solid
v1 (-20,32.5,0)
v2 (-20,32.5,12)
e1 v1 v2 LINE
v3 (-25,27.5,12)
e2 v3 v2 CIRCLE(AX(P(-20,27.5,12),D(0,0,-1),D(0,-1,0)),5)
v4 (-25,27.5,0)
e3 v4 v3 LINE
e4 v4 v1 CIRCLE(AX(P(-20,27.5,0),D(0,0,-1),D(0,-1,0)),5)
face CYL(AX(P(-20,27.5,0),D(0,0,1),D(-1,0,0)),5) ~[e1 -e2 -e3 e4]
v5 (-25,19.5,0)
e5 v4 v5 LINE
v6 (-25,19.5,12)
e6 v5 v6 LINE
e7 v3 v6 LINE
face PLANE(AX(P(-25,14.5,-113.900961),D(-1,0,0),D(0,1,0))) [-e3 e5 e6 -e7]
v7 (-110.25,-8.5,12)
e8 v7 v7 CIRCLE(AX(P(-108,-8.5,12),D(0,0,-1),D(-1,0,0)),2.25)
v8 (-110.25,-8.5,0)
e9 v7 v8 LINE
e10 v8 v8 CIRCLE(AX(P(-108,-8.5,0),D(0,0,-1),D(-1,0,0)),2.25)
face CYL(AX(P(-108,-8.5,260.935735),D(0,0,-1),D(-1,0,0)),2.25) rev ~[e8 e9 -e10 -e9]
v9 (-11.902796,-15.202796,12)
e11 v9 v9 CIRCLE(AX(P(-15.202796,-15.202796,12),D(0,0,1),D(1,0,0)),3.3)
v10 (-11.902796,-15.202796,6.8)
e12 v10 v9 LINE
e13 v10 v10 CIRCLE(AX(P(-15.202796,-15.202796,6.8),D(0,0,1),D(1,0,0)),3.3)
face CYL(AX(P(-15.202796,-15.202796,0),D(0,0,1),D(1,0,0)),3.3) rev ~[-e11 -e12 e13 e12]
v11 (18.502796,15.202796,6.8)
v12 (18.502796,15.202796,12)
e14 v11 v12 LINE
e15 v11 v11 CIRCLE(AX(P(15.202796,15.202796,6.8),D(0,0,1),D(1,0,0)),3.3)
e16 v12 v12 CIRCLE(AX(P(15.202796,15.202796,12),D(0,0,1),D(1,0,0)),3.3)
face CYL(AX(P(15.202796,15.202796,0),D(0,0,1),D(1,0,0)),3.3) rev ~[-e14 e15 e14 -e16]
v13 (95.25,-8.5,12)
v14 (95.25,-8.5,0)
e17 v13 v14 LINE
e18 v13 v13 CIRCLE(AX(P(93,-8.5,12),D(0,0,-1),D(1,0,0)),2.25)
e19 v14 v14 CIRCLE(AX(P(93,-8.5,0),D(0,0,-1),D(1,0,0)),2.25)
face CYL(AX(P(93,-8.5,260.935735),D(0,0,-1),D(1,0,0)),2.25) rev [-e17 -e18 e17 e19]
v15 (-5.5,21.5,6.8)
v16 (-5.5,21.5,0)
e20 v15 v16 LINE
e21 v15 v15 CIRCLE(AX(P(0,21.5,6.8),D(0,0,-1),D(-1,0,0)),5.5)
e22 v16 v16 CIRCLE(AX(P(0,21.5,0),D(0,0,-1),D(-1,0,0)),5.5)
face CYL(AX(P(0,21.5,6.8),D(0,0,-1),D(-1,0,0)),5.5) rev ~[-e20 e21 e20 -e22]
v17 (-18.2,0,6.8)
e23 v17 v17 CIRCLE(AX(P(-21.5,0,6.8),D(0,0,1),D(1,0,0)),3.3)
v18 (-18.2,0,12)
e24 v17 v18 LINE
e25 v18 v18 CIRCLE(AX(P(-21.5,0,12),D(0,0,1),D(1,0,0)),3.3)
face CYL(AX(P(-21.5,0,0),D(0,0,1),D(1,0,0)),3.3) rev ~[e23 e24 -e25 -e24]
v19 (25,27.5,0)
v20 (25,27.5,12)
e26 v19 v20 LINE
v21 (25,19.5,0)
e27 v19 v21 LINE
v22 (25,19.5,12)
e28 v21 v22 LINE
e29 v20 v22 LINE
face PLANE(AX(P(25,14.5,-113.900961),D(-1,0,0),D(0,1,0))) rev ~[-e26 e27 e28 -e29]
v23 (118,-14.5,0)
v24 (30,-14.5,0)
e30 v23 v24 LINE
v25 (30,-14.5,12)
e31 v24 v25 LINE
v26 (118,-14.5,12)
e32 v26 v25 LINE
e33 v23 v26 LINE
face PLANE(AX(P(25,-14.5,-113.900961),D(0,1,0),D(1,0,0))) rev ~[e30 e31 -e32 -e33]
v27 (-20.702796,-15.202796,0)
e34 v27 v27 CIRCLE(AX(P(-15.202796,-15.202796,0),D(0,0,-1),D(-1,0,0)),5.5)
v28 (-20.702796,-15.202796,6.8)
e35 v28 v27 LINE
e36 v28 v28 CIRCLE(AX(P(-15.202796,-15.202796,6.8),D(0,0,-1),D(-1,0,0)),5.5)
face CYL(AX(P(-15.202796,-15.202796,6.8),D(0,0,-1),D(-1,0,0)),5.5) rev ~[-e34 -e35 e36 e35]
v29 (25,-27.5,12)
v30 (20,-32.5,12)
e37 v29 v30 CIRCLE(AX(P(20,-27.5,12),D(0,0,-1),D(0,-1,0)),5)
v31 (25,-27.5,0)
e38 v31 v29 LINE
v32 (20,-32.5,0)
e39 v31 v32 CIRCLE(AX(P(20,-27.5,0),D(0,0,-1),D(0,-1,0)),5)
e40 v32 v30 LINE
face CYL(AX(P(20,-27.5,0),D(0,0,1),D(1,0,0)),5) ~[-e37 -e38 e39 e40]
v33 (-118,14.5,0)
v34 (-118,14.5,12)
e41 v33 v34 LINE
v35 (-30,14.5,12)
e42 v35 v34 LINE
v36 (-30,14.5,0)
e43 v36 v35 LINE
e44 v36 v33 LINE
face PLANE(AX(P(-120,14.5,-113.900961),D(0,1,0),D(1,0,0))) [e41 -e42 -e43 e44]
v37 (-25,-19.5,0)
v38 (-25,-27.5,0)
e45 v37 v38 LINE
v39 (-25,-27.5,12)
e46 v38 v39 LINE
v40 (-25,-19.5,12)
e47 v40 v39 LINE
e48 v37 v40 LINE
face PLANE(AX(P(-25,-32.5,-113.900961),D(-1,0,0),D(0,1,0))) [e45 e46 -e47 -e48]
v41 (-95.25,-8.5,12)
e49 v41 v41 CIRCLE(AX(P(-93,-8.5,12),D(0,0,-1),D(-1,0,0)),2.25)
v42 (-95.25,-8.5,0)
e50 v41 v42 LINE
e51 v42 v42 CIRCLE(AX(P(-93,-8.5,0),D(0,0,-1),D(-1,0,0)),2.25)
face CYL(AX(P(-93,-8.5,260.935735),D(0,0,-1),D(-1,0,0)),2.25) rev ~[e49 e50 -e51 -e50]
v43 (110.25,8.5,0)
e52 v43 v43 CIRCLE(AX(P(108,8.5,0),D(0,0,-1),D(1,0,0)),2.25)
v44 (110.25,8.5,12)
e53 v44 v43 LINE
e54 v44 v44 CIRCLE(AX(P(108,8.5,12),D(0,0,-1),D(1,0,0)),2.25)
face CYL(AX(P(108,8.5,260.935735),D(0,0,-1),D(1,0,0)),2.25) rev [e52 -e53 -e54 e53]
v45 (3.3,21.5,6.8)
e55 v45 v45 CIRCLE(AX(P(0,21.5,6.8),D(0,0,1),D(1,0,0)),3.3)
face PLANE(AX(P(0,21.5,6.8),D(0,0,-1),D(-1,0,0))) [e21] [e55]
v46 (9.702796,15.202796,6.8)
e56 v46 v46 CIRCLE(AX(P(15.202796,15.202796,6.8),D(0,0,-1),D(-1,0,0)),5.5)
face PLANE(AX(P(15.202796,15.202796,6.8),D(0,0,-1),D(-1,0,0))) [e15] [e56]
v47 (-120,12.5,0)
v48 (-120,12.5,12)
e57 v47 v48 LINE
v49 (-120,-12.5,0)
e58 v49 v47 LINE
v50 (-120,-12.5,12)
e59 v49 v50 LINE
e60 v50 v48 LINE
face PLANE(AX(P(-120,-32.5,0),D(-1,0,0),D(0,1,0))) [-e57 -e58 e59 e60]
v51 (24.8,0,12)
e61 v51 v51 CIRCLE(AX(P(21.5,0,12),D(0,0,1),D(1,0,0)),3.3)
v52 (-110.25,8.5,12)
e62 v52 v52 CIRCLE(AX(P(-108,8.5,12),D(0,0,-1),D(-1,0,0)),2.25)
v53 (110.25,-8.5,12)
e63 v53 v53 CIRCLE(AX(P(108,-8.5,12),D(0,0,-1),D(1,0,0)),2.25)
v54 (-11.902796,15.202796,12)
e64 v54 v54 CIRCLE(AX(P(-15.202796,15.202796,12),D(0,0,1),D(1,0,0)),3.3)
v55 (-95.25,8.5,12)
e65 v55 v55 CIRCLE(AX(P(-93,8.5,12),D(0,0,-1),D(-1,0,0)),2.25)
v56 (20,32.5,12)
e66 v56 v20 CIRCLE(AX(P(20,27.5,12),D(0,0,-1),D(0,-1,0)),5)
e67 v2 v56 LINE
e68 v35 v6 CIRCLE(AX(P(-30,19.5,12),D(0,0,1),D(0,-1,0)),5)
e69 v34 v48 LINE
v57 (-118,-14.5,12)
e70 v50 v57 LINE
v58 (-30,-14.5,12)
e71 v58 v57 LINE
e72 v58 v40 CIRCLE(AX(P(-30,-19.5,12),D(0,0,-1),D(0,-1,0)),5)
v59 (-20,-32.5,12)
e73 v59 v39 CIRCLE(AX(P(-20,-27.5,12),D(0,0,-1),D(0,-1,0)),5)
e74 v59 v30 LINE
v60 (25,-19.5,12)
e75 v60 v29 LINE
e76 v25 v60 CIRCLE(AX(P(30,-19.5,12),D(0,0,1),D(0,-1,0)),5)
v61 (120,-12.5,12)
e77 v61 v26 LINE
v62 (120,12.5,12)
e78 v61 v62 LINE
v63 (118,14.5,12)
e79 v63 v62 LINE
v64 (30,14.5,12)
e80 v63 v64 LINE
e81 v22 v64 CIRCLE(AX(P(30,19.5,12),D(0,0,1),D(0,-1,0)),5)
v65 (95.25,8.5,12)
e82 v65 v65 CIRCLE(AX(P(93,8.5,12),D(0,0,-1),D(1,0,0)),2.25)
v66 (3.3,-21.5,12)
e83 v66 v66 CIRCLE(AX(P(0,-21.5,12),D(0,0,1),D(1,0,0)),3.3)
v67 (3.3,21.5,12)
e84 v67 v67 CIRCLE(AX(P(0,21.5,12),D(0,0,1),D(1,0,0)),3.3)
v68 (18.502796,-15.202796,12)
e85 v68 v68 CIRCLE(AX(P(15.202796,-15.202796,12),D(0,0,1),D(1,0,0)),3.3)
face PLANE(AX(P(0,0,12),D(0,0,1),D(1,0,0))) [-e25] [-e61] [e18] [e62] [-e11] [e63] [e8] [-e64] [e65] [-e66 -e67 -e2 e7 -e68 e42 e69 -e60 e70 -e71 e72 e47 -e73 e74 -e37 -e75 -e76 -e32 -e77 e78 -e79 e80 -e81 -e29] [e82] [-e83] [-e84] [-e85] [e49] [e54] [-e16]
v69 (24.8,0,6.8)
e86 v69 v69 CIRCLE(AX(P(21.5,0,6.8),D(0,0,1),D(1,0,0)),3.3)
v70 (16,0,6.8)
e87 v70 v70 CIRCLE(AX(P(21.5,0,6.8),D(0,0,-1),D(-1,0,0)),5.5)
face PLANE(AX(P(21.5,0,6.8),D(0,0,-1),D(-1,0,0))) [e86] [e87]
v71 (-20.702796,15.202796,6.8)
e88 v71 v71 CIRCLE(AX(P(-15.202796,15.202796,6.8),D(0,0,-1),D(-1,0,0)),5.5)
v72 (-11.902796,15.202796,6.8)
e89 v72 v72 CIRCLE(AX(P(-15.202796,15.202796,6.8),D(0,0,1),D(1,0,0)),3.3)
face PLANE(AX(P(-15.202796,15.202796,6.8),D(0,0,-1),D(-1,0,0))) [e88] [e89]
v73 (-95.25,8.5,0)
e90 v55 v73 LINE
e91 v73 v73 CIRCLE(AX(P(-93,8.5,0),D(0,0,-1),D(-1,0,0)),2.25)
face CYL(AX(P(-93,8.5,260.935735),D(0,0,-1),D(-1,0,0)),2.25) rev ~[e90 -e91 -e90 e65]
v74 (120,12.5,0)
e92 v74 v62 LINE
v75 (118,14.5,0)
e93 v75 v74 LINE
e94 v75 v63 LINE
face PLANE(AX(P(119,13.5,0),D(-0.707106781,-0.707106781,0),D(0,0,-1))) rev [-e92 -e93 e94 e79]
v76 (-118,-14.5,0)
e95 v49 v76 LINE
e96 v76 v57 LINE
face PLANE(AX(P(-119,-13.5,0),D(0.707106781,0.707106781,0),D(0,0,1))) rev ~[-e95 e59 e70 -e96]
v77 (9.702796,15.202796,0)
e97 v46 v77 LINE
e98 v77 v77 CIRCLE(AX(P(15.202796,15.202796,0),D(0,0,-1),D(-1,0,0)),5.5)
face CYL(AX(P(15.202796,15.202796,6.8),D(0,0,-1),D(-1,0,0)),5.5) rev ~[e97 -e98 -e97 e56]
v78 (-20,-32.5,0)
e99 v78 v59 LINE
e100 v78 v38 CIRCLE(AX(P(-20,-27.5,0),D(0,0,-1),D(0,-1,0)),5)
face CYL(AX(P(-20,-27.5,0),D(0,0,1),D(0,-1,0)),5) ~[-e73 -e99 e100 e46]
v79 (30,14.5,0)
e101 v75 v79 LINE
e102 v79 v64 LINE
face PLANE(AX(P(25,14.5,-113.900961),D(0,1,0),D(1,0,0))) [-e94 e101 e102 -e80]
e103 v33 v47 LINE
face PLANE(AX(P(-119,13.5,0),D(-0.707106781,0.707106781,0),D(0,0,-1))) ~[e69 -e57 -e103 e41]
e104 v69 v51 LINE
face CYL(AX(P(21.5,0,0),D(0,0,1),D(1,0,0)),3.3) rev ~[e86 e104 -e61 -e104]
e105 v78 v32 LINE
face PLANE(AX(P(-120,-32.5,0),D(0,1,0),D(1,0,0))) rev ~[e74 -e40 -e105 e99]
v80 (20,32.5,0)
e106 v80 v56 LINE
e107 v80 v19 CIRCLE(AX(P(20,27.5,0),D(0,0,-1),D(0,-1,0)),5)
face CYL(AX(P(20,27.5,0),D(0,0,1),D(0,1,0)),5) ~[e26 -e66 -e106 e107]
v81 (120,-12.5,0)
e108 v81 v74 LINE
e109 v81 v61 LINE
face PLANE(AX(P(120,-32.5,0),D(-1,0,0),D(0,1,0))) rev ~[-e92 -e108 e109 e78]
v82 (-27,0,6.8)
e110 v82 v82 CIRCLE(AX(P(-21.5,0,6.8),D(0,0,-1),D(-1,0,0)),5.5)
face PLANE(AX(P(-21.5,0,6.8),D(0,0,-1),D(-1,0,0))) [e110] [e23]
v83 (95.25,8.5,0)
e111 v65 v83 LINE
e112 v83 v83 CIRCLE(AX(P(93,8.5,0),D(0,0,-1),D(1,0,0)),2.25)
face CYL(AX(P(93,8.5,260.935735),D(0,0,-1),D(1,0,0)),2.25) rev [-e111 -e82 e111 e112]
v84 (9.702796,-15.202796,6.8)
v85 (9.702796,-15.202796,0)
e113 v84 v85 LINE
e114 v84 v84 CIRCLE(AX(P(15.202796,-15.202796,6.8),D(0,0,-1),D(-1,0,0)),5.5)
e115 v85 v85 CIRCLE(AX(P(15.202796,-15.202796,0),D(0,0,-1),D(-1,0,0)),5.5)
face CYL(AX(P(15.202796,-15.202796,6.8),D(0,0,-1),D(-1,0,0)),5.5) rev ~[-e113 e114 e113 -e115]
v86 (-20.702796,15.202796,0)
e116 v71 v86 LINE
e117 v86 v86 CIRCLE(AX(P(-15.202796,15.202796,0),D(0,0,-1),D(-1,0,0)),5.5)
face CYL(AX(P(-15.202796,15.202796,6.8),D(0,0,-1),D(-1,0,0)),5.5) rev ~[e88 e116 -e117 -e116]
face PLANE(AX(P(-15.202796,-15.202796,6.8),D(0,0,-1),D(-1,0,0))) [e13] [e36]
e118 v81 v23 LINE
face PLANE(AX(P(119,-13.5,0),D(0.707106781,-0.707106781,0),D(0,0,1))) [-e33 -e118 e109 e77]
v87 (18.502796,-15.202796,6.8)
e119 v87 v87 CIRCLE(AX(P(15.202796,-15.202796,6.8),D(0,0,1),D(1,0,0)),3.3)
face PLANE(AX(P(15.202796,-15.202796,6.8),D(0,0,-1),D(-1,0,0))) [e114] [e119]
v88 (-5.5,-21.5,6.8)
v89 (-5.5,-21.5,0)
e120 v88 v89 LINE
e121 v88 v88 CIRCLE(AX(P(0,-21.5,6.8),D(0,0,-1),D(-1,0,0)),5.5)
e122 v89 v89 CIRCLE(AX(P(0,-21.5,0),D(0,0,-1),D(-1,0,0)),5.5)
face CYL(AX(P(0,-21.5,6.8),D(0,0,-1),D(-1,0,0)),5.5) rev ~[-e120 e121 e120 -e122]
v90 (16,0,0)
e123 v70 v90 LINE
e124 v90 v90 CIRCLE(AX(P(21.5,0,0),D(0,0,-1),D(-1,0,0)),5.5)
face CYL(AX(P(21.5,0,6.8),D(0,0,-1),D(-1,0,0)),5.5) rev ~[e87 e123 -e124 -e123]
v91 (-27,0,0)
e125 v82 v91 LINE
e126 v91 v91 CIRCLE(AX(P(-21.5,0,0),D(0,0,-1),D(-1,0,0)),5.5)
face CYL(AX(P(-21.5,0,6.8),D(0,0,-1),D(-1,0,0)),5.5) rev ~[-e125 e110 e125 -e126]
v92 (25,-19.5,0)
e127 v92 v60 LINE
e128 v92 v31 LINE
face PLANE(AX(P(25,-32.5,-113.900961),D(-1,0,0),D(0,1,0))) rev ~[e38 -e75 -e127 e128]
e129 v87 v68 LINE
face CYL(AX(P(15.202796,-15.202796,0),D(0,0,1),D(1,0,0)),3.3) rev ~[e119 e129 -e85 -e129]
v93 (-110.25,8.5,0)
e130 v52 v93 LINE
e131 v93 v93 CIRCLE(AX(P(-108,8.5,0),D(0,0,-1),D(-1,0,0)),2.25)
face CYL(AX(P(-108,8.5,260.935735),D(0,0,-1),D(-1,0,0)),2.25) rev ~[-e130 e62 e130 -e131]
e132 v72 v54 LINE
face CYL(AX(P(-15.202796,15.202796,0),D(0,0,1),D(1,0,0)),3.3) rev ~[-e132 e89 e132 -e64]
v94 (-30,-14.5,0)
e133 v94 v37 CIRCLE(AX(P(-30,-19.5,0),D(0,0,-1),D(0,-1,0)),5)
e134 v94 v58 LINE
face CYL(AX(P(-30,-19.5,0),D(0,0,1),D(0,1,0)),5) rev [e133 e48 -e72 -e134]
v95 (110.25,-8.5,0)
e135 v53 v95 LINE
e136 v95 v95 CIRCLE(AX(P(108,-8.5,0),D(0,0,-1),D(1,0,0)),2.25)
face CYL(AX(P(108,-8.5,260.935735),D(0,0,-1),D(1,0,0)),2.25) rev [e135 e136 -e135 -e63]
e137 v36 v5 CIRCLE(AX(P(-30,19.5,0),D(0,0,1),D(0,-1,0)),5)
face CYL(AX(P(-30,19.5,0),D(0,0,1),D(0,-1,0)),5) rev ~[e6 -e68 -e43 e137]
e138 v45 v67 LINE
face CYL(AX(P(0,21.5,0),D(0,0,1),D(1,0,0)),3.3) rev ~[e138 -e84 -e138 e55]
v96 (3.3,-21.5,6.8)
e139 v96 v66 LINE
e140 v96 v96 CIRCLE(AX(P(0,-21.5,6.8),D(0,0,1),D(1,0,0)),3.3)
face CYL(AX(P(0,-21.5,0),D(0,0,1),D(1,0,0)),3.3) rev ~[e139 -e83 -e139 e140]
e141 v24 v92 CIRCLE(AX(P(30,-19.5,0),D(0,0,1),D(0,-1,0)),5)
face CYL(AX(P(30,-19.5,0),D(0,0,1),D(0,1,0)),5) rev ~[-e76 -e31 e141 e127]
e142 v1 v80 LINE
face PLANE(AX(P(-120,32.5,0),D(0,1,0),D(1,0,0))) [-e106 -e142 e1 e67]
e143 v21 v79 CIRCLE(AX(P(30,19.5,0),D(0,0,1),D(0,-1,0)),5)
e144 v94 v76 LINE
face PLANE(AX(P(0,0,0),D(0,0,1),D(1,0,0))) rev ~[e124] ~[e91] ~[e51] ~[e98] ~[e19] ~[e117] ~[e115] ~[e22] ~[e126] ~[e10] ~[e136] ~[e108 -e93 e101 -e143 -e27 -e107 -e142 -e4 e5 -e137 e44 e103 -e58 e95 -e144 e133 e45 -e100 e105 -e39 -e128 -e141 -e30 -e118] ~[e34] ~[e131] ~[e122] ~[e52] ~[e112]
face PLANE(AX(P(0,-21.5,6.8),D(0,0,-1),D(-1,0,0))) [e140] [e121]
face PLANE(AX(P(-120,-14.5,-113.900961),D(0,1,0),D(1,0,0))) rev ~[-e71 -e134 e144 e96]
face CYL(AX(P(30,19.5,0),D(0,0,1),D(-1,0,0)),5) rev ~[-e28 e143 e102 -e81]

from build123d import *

# Parameters (mm, degrees)
SKETCH1_W                                        = 240
SKETCH1_H                                        = 65
BOSS_EXTRUDE1_DEPTH                              = 12
CUT_EXTRUDE1_DEPTH                               = 125.900960765
CUT_EXTRUDE1_DEPTH_BACK                          = 125.900960765
SKETCH2_W                                        = 95
SKETCH2_H                                        = 18
FILLET1_R                                        = 5
HOLE_FOR_SOCKET_HEAD_CAP_SCREW_TYPE1_D           = 6.6
HOLE_FOR_SOCKET_HEAD_CAP_SCREW_TYPE1_CBORE_D     = 11
HOLE_FOR_SOCKET_HEAD_CAP_SCREW_TYPE1_CBORE_DEPTH = 6.8
F_4_5_4_5_DIAMETER_HOLE1_D                       = 4.5
CHAMFER1_SIZE                                    = 2


with BuildPart() as part:
    # Sketch1 → Boss-Extrude1 (new body)
    with BuildSketch(Plane.XY):
        Rectangle(SKETCH1_W, SKETCH1_H)
    extrude(amount=BOSS_EXTRUDE1_DEPTH)

    # Sketch2 → Cut-Extrude1 (cut, two sides: drawn at the far end of the back side and taken through both)
    with BuildSketch(Plane.XY.offset(12).offset(-CUT_EXTRUDE1_DEPTH_BACK)):
        with Locations((-72.5, 23.5)):
            Rectangle(SKETCH2_W, SKETCH2_H)
        with Locations((72.5, 23.5)):
            Rectangle(SKETCH2_W, SKETCH2_H)
        with Locations((72.5, -23.5)):
            Rectangle(SKETCH2_W, SKETCH2_H)
        with Locations((-72.5, -23.5)):
            Rectangle(SKETCH2_W, SKETCH2_H)
    extrude(amount=CUT_EXTRUDE1_DEPTH + CUT_EXTRUDE1_DEPTH_BACK, mode=Mode.SUBTRACT)

    # Fillet1
    fillet1_edges = [part.edges().sort_by_distance(p)[0] for p in [
        (-25, -32.5, 6),
        (-25, -14.5, 6),
        (25, -32.5, 6),
        (25, -14.5, 6),
        (25, 32.5, 6),
        (25, 14.5, 6),
        (-25, 32.5, 6),
        (-25, 14.5, 6),
    ]]
    fillet(fillet1_edges, radius=FILLET1_R)

    # Hole for socket head cap screw, type1 (through all)
    with Locations(Plane(origin=(0, 0, 0), x_dir=(-1, 0, 0), z_dir=(0, 0, -1))):
        with Locations((15.202795796, -15.202795796), (0, -21.5), (-15.202795796, -15.202795796), (-21.5, 0), (-15.202795796, 15.202795796), (0, 21.5), (15.202795796, 15.202795796), (21.5, 0)):
            CounterBoreHole(HOLE_FOR_SOCKET_HEAD_CAP_SCREW_TYPE1_D / 2, HOLE_FOR_SOCKET_HEAD_CAP_SCREW_TYPE1_CBORE_D / 2, HOLE_FOR_SOCKET_HEAD_CAP_SCREW_TYPE1_CBORE_DEPTH)

    # Ø4.5 (4.5) Diameter Hole1 (through all)
    with Locations(Plane.XY.offset(12)):
        with Locations((-93, -8.5), (-108, -8.5), (-93, 8.5), (-108, 8.5)):
            f_4_5_4_5_diameter_hole1 = Hole(F_4_5_4_5_DIAMETER_HOLE1_D / 2)

    # Mirror1: Ø4.5 (4.5) Diameter Hole1 across plane
    add(f_4_5_4_5_diameter_hole1.mirror(Plane(origin=(0, 0, 0), x_dir=(0, 0, 1), z_dir=(1, 0, 0))), mode=Mode.SUBTRACT)

    # Chamfer1
    chamfer1_edges = [part.edges().sort_by_distance(p)[0] for p in [
        (-120, -14.5, 6),
        (120, -14.5, 6),
        (120, 14.5, 6),
        (-120, 14.5, 6),
    ]]
    chamfer(chamfer1_edges, length=CHAMFER1_SIZE)


solid = part.part
